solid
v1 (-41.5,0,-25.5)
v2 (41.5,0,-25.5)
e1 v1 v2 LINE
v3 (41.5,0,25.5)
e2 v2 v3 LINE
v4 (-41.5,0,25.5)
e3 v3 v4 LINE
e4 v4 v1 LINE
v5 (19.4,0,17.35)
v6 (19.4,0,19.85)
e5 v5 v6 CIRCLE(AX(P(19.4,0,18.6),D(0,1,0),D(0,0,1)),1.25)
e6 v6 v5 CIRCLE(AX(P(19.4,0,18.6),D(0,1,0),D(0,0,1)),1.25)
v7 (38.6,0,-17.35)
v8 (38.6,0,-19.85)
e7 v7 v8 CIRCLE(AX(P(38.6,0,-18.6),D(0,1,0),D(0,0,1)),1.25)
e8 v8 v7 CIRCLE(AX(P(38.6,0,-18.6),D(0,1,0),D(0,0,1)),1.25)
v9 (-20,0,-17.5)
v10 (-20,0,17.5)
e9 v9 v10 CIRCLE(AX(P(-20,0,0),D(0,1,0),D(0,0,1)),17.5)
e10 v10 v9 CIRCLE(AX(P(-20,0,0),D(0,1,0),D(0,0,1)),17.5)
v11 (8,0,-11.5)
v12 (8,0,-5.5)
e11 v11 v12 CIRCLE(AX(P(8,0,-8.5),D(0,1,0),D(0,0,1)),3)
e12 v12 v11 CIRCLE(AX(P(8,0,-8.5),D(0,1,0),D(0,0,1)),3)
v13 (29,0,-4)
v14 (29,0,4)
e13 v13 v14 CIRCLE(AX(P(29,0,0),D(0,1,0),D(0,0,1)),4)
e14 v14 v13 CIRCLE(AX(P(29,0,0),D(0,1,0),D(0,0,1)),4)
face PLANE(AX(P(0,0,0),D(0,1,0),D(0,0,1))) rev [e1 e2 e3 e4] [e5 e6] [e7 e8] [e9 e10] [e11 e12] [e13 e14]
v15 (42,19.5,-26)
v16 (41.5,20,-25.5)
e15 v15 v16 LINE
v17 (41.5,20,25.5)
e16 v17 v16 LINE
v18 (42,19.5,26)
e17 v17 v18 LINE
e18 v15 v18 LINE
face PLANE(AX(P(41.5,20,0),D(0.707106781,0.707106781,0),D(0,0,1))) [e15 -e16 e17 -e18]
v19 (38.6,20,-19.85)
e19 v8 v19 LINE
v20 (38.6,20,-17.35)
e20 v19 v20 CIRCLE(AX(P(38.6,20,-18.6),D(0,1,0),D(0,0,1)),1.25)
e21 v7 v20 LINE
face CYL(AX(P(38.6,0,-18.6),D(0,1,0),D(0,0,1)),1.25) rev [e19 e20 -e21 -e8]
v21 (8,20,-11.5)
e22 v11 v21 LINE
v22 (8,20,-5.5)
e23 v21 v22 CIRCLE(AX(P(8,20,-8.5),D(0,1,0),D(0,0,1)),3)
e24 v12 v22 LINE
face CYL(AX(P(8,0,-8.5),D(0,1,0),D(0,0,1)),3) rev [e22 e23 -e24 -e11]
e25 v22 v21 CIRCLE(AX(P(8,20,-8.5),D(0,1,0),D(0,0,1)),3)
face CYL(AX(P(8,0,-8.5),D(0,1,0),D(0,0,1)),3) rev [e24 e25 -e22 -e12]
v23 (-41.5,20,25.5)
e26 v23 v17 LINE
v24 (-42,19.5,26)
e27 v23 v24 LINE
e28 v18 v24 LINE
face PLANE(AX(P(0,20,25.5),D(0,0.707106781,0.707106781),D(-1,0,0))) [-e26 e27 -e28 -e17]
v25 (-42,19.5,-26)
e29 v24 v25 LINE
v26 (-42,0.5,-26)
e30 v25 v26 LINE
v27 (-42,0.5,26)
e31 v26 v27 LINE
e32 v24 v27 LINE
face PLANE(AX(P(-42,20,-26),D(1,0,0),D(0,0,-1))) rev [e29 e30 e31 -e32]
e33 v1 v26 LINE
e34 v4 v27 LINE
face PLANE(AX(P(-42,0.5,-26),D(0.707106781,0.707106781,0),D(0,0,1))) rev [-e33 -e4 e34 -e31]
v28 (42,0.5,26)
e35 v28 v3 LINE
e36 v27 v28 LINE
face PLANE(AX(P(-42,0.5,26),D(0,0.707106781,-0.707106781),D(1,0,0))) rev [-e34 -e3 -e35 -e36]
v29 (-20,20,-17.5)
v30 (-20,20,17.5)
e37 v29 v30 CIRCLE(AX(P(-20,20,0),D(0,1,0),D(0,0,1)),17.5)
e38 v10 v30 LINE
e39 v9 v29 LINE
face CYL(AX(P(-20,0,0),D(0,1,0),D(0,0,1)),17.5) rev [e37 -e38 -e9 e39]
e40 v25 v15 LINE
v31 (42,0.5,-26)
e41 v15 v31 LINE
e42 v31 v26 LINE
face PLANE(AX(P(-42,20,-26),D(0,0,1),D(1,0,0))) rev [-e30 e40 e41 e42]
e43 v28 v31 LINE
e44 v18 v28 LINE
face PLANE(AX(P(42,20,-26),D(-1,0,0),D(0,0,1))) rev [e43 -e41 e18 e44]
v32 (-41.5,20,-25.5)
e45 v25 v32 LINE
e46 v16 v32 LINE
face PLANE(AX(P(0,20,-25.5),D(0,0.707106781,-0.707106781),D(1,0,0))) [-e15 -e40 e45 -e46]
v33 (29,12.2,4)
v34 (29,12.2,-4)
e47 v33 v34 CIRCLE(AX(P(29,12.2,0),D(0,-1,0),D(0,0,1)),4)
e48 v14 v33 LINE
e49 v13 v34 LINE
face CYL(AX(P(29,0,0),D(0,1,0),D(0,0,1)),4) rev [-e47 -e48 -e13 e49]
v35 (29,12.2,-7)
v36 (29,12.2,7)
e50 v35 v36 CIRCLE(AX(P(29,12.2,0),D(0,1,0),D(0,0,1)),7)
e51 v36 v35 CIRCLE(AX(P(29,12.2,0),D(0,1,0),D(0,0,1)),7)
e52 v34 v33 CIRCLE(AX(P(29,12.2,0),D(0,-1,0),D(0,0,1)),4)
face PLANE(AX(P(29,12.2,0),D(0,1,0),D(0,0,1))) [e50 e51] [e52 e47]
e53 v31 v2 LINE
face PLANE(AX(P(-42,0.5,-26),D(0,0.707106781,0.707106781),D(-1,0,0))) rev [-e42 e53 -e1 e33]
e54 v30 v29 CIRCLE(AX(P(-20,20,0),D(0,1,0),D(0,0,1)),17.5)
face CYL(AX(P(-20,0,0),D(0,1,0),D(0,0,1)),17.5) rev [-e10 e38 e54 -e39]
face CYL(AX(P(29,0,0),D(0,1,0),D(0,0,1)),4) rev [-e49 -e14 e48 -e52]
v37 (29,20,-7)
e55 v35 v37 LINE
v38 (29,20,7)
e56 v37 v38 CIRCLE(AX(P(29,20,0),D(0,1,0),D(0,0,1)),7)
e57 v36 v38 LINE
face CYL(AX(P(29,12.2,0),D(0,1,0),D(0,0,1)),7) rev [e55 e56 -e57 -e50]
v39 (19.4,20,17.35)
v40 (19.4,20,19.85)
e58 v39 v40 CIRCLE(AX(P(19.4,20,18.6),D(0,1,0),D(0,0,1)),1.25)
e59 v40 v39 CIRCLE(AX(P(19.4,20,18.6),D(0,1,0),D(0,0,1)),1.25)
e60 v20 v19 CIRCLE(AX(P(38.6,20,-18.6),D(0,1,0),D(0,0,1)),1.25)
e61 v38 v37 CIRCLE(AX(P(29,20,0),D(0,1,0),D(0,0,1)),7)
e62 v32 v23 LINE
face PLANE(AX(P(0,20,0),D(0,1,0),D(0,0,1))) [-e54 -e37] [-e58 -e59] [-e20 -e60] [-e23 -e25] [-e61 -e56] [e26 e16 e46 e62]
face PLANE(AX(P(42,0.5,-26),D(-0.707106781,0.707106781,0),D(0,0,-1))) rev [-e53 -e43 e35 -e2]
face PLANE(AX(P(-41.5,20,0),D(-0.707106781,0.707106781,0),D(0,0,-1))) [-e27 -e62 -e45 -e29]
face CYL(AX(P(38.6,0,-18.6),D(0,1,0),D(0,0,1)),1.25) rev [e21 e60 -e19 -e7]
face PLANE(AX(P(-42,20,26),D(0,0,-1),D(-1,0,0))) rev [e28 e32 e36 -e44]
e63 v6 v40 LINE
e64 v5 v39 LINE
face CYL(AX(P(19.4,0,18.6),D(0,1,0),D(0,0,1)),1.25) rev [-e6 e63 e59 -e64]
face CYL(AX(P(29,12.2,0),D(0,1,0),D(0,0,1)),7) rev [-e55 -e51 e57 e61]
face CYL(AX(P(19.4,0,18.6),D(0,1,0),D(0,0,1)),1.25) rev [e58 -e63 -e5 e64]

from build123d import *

# Parameters (mm, degrees)
SKETCH1_W           = 84
SKETCH1_H           = 52
BOSS_EXTRUDE1_DEPTH = 20
SKETCH2_R           = 17.5
CUT_EXTRUDE1_DEPTH  = 20
SKETCH3_R           = 3
CUT_EXTRUDE2_DEPTH  = 20
SKETCH4_R           = 1.25
CUT_EXTRUDE3_DEPTH  = 20
SKETCH5_R           = 4
CUT_EXTRUDE4_DEPTH  = 20
SKETCH6_R           = 7
CUT_EXTRUDE5_DEPTH  = 7.8
CHAMFER1_SIZE       = 0.5


with BuildPart() as part:
    # Sketch1 → Boss-Extrude1 (new body)
    with BuildSketch(Plane(origin=(0, 0, 0), x_dir=(1, 0, 0), z_dir=(0, 1, 0))):
        Rectangle(SKETCH1_W, SKETCH1_H)
    extrude(amount=BOSS_EXTRUDE1_DEPTH)

    # Sketch2 → Cut-Extrude1 (cut)
    with BuildSketch(Plane(origin=(0, 20, 0), x_dir=(1, 0, 0), z_dir=(0, 1, 0))):
        with Locations(Location((-20, 0, 0), (0, 0, 270))):
            Circle(SKETCH2_R)
    extrude(amount=-CUT_EXTRUDE1_DEPTH, mode=Mode.SUBTRACT)

    # Sketch3 → Cut-Extrude2 (cut)
    with BuildSketch(Plane(origin=(0, 20, 0), x_dir=(1, 0, 0), z_dir=(0, 1, 0))):
        with Locations(Location((8, 8.5, 0), (0, 0, 270))):
            Circle(SKETCH3_R)
    extrude(amount=-CUT_EXTRUDE2_DEPTH, mode=Mode.SUBTRACT)

    # Sketch4 → Cut-Extrude3 (cut)
    with BuildSketch(Plane(origin=(0, 20, 0), x_dir=(1, 0, 0), z_dir=(0, 1, 0))):
        with Locations(Location((19.4, -18.6, 0), (0, 0, 270))):
            Circle(SKETCH4_R)
        with Locations(Location((38.6, 18.6, 0), (0, 0, 270))):
            Circle(SKETCH4_R)
    extrude(amount=-CUT_EXTRUDE3_DEPTH, mode=Mode.SUBTRACT)

    # Sketch5 → Cut-Extrude4 (cut)
    with BuildSketch(Plane(origin=(0, 20, 0), x_dir=(1, 0, 0), z_dir=(0, 1, 0))):
        with Locations(Location((29, 0, 0), (0, 0, 270))):
            Circle(SKETCH5_R)
    extrude(amount=-CUT_EXTRUDE4_DEPTH, mode=Mode.SUBTRACT)

    # Sketch6 → Cut-Extrude5 (cut)
    with BuildSketch(Plane(origin=(0, 20, 0), x_dir=(1, 0, 0), z_dir=(0, 1, 0))):
        with Locations(Location((29, 0, 0), (0, 0, 270))):
            Circle(SKETCH6_R)
    extrude(amount=-CUT_EXTRUDE5_DEPTH, mode=Mode.SUBTRACT)

    # Chamfer1
    chamfer1_edges = [part.edges().sort_by_distance(p)[0] for p in [
        (-42, 20, 0),
        (0, 20, 26),
        (42, 20, 0),
        (0, 0, 26),
        (-42, 0, 0),
        (0, 0, -26),
        (42, 0, 0),
        (0, 20, -26),
    ]]
    chamfer(chamfer1_edges, length=CHAMFER1_SIZE)


solid = part.part
